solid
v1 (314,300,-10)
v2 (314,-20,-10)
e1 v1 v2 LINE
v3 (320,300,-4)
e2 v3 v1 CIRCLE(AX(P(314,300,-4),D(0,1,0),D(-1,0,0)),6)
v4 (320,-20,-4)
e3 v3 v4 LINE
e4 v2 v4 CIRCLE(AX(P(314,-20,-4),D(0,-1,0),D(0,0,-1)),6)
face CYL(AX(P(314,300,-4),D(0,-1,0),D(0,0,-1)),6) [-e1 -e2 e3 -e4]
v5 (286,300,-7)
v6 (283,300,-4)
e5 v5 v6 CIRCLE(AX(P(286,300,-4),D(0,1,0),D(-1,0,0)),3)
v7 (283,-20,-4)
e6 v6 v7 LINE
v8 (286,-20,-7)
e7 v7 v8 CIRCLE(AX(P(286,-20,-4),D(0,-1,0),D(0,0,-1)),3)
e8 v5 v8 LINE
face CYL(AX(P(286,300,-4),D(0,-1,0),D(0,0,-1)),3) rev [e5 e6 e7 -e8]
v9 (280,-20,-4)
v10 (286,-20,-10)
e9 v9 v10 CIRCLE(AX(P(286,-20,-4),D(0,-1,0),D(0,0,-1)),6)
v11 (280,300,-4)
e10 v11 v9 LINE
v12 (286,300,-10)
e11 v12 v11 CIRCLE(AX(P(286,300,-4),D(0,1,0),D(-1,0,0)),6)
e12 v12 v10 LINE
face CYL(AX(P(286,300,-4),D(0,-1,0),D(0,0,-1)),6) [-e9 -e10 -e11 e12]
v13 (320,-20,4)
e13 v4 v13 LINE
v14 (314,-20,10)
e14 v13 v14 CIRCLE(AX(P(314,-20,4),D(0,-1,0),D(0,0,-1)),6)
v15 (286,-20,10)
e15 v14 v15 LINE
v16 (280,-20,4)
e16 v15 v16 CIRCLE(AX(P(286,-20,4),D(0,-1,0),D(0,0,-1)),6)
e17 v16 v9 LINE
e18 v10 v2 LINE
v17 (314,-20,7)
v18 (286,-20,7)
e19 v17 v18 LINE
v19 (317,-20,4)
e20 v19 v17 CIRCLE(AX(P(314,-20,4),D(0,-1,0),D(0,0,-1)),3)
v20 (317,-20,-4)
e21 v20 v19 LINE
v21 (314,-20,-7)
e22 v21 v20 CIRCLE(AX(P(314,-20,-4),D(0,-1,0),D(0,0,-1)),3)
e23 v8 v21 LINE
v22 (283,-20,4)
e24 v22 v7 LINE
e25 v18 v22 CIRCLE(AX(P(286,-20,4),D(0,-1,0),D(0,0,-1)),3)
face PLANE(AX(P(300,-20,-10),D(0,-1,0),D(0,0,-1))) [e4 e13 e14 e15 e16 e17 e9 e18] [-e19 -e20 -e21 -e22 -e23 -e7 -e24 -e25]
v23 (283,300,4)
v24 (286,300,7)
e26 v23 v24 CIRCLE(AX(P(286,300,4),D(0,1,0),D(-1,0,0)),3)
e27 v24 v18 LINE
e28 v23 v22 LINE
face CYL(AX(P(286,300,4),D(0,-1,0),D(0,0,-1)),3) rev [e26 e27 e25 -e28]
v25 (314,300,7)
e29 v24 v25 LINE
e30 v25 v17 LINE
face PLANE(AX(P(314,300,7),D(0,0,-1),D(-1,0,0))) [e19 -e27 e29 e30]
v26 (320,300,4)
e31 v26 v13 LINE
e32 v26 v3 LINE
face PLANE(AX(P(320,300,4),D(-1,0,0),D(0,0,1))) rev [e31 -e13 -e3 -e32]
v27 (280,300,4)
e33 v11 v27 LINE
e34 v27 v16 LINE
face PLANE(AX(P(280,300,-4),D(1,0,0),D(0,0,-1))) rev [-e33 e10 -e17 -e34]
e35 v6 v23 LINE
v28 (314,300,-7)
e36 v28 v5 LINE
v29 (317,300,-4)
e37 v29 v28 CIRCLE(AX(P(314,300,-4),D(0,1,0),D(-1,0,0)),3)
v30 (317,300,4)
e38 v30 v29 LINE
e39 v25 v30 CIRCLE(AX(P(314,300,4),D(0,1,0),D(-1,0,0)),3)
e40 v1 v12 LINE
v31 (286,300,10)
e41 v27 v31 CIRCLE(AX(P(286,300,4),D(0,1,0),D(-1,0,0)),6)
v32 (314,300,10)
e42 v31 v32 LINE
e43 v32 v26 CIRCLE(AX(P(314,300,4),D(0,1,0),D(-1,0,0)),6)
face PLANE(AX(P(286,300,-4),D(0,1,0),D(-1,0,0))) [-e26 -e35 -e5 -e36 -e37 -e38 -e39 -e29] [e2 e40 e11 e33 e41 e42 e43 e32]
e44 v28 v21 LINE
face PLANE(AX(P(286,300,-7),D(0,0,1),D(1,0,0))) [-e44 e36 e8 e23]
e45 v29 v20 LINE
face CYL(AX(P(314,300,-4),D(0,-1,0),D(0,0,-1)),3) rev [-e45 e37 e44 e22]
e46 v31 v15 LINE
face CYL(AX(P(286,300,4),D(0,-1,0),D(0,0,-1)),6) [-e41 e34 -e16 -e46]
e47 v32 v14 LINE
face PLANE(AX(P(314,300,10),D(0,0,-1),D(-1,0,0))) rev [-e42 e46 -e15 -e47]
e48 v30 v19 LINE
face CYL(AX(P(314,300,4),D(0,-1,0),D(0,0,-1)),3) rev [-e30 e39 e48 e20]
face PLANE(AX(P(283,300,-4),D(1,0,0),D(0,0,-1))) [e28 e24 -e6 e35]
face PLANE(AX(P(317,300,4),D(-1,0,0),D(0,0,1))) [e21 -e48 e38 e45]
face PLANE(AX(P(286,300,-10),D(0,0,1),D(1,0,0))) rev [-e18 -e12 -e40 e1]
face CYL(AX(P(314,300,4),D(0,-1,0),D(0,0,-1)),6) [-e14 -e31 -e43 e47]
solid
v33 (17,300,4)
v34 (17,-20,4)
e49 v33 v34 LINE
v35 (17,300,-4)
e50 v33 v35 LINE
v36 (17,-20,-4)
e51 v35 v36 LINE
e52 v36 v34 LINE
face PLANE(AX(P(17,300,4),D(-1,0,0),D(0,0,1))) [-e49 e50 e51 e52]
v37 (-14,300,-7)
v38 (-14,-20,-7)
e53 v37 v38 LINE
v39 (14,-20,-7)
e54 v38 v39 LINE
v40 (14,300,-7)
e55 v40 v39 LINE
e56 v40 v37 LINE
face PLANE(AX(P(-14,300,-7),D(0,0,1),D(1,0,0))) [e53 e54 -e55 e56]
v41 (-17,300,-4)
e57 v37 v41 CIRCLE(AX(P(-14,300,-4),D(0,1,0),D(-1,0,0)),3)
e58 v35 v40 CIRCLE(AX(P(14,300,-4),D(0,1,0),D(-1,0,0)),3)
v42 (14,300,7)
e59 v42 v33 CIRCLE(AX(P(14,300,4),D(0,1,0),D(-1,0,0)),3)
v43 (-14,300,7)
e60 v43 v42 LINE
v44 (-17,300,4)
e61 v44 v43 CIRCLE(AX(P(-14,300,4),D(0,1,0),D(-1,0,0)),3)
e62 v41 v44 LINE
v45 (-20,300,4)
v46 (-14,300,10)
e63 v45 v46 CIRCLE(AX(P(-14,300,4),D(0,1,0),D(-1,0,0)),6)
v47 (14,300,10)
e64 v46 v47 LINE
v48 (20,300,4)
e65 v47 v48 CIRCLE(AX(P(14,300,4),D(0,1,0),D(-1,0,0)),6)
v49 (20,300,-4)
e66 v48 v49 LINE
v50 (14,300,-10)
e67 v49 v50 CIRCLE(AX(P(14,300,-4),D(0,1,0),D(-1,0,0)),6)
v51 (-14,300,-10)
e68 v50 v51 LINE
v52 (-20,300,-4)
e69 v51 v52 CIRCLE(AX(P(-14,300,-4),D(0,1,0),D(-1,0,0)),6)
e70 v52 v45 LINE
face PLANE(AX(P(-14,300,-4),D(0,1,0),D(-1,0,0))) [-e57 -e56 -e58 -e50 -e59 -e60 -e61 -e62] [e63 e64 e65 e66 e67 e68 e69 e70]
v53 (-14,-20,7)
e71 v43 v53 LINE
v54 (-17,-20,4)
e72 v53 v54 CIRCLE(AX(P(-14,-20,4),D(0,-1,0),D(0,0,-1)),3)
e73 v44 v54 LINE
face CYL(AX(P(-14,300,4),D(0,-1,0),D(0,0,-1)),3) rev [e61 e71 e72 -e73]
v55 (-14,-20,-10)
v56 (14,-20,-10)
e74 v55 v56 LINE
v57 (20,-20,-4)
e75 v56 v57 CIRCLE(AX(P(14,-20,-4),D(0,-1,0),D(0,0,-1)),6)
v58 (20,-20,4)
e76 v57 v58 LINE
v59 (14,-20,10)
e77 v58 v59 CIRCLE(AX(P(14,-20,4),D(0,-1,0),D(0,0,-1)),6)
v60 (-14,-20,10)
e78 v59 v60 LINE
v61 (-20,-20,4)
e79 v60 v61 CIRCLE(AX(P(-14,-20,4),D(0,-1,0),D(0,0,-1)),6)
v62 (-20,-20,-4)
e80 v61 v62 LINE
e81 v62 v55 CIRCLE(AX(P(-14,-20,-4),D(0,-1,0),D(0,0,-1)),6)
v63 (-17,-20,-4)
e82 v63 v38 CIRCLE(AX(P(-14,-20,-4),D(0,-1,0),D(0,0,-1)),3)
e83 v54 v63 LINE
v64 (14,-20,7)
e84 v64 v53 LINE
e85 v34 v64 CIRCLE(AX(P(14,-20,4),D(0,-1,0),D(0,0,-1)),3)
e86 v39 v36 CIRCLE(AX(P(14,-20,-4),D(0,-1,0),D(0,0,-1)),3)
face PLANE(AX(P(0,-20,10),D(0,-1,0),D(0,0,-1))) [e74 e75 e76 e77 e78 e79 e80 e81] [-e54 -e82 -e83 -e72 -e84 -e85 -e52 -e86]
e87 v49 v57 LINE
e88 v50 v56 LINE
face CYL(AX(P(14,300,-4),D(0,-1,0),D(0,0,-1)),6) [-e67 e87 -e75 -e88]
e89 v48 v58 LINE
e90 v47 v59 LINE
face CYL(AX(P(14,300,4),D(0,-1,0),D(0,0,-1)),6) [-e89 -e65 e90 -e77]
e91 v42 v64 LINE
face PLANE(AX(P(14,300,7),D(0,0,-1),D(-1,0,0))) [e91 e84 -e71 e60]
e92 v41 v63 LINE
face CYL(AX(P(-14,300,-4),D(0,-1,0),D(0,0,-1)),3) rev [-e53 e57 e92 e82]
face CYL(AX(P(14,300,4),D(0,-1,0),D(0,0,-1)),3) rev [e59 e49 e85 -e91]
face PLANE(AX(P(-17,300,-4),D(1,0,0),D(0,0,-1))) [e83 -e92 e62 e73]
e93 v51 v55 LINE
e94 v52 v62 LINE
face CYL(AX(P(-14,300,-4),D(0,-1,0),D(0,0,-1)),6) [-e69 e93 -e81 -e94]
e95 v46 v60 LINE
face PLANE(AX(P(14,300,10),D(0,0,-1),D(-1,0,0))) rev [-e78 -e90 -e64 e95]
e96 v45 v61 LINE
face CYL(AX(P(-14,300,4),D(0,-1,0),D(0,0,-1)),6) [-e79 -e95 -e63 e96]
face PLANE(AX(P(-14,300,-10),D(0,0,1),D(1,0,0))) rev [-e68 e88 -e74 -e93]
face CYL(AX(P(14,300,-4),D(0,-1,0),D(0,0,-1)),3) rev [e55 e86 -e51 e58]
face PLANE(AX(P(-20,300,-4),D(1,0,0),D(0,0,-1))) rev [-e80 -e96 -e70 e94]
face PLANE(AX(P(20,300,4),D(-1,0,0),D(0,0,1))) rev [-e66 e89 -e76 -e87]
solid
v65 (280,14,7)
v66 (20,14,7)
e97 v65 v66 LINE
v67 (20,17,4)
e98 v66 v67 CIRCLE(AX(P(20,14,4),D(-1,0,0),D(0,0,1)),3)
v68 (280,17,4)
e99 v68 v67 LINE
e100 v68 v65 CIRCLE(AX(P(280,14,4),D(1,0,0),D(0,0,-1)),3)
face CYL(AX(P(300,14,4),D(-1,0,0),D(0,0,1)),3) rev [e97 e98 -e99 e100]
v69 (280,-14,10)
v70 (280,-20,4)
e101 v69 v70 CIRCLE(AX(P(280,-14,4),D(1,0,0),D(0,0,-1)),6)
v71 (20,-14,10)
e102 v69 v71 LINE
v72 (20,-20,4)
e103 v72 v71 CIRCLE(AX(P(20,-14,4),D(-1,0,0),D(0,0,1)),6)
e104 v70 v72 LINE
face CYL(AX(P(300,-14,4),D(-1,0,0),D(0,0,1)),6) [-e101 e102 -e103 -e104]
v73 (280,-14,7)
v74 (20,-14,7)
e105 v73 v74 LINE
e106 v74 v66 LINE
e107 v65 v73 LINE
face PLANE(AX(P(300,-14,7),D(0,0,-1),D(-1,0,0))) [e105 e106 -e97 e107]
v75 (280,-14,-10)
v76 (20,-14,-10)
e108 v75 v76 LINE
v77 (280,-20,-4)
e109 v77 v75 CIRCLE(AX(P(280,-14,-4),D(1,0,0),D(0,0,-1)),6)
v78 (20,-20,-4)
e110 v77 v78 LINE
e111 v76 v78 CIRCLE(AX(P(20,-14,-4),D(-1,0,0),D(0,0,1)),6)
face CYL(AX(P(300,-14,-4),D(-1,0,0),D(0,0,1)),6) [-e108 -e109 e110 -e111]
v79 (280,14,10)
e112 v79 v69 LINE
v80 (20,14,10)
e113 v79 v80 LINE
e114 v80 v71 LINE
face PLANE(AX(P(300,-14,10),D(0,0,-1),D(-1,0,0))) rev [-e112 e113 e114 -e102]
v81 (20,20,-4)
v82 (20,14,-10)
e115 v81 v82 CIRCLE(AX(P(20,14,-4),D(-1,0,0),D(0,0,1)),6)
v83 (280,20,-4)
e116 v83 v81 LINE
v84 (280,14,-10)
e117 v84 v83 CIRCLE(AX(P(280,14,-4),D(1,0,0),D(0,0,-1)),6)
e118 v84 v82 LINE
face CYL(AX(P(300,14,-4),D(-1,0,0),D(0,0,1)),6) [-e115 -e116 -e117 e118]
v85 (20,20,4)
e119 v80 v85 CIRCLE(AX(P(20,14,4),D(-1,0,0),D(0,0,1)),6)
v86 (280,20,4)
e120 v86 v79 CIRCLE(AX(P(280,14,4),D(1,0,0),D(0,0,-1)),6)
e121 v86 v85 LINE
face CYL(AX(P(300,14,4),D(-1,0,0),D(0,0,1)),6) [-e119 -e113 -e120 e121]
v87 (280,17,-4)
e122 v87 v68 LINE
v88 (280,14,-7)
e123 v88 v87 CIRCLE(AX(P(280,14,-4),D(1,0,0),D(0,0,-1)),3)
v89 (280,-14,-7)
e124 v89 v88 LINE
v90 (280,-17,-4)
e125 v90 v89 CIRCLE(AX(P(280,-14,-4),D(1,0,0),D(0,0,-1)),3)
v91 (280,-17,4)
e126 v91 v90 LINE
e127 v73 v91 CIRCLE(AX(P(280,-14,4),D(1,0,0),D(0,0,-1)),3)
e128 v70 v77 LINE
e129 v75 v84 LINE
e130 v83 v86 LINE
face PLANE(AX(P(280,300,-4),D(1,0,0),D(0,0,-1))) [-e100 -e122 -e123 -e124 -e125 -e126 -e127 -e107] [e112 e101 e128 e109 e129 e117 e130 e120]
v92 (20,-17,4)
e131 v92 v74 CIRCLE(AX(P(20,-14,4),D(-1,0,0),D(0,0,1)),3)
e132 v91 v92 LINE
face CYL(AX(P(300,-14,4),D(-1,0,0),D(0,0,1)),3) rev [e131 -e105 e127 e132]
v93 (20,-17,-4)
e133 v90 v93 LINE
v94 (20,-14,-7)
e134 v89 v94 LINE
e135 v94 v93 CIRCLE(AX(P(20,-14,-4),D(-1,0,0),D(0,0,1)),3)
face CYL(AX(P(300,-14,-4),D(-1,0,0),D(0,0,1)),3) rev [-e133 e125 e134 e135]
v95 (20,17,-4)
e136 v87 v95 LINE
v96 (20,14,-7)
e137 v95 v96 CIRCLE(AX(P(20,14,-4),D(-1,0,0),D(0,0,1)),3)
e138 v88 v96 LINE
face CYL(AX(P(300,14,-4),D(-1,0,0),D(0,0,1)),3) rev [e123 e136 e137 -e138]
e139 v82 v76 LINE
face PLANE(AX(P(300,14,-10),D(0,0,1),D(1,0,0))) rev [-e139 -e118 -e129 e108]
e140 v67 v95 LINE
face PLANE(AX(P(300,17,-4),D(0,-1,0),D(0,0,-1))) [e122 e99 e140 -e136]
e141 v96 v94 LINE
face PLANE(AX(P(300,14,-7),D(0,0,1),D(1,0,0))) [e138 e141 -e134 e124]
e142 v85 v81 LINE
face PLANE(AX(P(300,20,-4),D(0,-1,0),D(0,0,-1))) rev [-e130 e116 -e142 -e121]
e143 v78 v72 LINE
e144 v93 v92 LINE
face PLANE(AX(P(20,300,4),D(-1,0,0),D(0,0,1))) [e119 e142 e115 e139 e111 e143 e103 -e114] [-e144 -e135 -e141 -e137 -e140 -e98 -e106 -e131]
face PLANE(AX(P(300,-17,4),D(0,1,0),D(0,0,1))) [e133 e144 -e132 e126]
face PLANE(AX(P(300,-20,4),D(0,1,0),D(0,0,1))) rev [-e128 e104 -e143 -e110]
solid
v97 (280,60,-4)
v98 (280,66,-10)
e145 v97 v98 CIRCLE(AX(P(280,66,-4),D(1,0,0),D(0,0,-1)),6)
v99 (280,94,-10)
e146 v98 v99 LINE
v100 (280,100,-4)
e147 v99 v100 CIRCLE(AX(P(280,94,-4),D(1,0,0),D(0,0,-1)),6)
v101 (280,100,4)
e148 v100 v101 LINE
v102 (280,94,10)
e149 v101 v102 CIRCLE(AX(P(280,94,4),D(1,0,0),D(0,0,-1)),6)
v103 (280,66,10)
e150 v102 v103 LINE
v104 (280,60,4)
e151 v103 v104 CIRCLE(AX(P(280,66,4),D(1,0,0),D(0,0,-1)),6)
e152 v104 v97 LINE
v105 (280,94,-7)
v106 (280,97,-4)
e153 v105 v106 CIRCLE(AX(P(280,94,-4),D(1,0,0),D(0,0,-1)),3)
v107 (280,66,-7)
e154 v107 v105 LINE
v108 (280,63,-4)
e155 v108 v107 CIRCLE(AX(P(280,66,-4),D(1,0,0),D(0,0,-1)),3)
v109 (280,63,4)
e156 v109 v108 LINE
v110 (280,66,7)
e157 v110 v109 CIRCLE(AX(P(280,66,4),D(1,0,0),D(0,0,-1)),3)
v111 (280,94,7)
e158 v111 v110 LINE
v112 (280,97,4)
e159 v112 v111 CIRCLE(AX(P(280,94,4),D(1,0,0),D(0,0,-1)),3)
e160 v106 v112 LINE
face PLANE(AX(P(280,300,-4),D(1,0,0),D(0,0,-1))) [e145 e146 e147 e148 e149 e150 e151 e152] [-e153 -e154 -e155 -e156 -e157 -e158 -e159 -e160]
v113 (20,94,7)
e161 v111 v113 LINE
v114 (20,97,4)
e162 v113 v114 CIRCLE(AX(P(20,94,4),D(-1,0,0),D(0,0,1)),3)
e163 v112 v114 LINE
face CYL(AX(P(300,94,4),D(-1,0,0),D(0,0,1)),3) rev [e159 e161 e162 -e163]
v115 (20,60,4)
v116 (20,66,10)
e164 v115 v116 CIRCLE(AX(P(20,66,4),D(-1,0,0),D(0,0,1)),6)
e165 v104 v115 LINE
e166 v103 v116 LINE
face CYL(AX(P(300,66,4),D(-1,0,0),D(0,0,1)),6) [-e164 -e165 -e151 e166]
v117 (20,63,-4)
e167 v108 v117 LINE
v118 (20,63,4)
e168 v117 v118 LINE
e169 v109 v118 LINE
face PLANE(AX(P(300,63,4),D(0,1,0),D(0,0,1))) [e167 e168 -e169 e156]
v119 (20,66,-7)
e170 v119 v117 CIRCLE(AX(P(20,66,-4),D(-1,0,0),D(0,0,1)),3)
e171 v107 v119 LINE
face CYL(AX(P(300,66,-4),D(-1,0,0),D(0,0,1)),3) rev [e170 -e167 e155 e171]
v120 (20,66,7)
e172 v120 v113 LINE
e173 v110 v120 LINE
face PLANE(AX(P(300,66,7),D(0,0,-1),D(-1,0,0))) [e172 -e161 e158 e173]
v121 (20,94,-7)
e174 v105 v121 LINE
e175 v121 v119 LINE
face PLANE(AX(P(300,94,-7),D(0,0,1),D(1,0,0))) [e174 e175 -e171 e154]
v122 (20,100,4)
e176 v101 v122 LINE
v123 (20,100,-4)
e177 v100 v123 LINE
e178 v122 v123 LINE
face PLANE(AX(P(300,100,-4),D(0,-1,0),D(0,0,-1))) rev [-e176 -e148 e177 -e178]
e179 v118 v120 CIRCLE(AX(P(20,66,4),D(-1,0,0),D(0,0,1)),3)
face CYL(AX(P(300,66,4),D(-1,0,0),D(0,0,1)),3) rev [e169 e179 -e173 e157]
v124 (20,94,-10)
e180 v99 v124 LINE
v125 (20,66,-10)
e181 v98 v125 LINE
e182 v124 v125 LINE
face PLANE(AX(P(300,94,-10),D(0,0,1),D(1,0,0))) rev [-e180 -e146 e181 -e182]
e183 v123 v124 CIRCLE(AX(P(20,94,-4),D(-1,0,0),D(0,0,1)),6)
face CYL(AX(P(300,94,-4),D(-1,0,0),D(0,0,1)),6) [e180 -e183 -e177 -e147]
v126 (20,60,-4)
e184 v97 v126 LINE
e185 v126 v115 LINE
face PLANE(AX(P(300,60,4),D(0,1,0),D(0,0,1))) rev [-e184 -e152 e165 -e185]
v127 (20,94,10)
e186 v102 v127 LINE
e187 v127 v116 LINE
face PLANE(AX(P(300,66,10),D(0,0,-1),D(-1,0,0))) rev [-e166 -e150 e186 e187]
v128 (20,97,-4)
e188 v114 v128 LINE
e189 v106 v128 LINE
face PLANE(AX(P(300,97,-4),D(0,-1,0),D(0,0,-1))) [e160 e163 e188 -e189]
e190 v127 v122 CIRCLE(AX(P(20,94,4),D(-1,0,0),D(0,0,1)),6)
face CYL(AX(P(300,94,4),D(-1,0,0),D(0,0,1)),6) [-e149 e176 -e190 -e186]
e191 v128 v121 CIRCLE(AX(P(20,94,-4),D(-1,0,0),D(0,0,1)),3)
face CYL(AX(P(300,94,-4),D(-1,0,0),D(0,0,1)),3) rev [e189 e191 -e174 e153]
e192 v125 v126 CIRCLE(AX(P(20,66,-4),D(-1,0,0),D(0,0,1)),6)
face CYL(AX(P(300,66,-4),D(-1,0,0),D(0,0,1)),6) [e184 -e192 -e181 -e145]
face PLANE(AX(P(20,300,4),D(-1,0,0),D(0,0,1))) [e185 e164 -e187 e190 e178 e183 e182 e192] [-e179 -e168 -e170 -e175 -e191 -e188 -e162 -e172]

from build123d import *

# Parameters (mm, degrees)
F_40_X_20_X_3_1_DEPTH      = 300
F_40_X_20_X_3_1_DEPTH_BACK = 20
F_40_X_20_X_3_1_2_DEPTH    = 320
F_40_X_20_X_3_1_3_DEPTH    = 302
F_40_X_20_X_3_1_4_DEPTH    = 302


with BuildPart() as part:
    # Sketch1 → 矩形管 40 X 20 X 3(1) (new, two sides: drawn at the far end of the back side and taken through both)
    with BuildSketch(Plane(origin=(0, 0, 0), x_dir=(0, 0, -1), z_dir=(0, 1, 0)).offset(-F_40_X_20_X_3_1_DEPTH_BACK)):
        with BuildLine():
            Line((-4, -20), (4, -20))
            ThreePointArc((4, -20), (8.242640687, -18.242640687), (10, -14))
            Line((10, -14), (10, 14))
            ThreePointArc((10, 14), (8.242640687, 18.242640687), (4, 20))
            Line((4, 20), (-4, 20))
            ThreePointArc((-4, 20), (-8.242640687, 18.242640687), (-10, 14))
            Line((-10, 14), (-10, -14))
            ThreePointArc((-10, -14), (-8.242640687, -18.242640687), (-4, -20))
        make_face()
        with BuildLine():
            Line((-4, -17), (4, -17))
            ThreePointArc((4, -17), (6.121320344, -16.121320344), (7, -14))
            Line((7, -14), (7, 14))
            ThreePointArc((7, 14), (6.121320344, 16.121320344), (4, 17))
            Line((4, 17), (-4, 17))
            ThreePointArc((-4, 17), (-6.121320344, 16.121320344), (-7, 14))
            Line((-7, 14), (-7, -14))
            ThreePointArc((-7, -14), (-6.121320344, -16.121320344), (-4, -17))
        make_face(mode=Mode.SUBTRACT)
    extrude(amount=F_40_X_20_X_3_1_DEPTH + F_40_X_20_X_3_1_DEPTH_BACK)


with BuildPart() as body_2:
    # Sketch1 on segment 2 (carried to segment 2) → 40 X 20 X 3_1 2 (new body)
    with BuildSketch(Plane(origin=(300, -20, 0), x_dir=(0, 0, -1), z_dir=(0, 1, 0))):
        with BuildLine():
            Line((-4, -20), (4, -20))
            ThreePointArc((4, -20), (8.242640687, -18.242640687), (10, -14))
            Line((10, -14), (10, 14))
            ThreePointArc((10, 14), (8.242640687, 18.242640687), (4, 20))
            Line((4, 20), (-4, 20))
            ThreePointArc((-4, 20), (-8.242640687, 18.242640687), (-10, 14))
            Line((-10, 14), (-10, -14))
            ThreePointArc((-10, -14), (-8.242640687, -18.242640687), (-4, -20))
        make_face()
        with BuildLine():
            Line((-4, -17), (4, -17))
            ThreePointArc((4, -17), (6.121320344, -16.121320344), (7, -14))
            Line((7, -14), (7, 14))
            ThreePointArc((7, 14), (6.121320344, 16.121320344), (4, 17))
            Line((4, 17), (-4, 17))
            ThreePointArc((-4, 17), (-6.121320344, 16.121320344), (-7, 14))
            Line((-7, 14), (-7, -14))
            ThreePointArc((-7, -14), (-6.121320344, -16.121320344), (-4, -17))
        make_face(mode=Mode.SUBTRACT)
    extrude(amount=F_40_X_20_X_3_1_2_DEPTH)


with BuildPart() as body_3:
    # Sketch1 on segment 3 (carried to segment 3) → 40 X 20 X 3_1 3 (new body)
    with BuildSketch(Plane(origin=(-1, 0, 0), x_dir=(0, 0, -1), z_dir=(1, 0, 0))):
        with BuildLine():
            Line((-4, -20), (4, -20))
            ThreePointArc((4, -20), (8.242640687, -18.242640687), (10, -14))
            Line((10, -14), (10, 14))
            ThreePointArc((10, 14), (8.242640687, 18.242640687), (4, 20))
            Line((4, 20), (-4, 20))
            ThreePointArc((-4, 20), (-8.242640687, 18.242640687), (-10, 14))
            Line((-10, 14), (-10, -14))
            ThreePointArc((-10, -14), (-8.242640687, -18.242640687), (-4, -20))
        make_face()
        with BuildLine():
            Line((-4, -17), (4, -17))
            ThreePointArc((4, -17), (6.121320344, -16.121320344), (7, -14))
            Line((7, -14), (7, 14))
            ThreePointArc((7, 14), (6.121320344, 16.121320344), (4, 17))
            Line((4, 17), (-4, 17))
            ThreePointArc((-4, 17), (-6.121320344, 16.121320344), (-7, 14))
            Line((-7, 14), (-7, -14))
            ThreePointArc((-7, -14), (-6.121320344, -16.121320344), (-4, -17))
        make_face(mode=Mode.SUBTRACT)
    extrude(amount=F_40_X_20_X_3_1_3_DEPTH)

    # 40 X 20 X 3_1 3 end butt 1
    split(bisect_by=Plane.YZ.offset(20), keep=Keep.TOP)

    # 40 X 20 X 3_1 3 end butt 2
    split(bisect_by=Plane(origin=(280, 0, 0), x_dir=(0, -1, 0), z_dir=(-1, 0, 0)), keep=Keep.TOP)


with BuildPart() as body_4:
    # Sketch1 on segment 4 (carried to segment 4) → 40 X 20 X 3_1 4 (new body)
    with BuildSketch(Plane(origin=(-1, 80, 0), x_dir=(0, 0, -1), z_dir=(1, 0, 0))):
        with BuildLine():
            Line((-4, -20), (4, -20))
            ThreePointArc((4, -20), (8.242640687, -18.242640687), (10, -14))
            Line((10, -14), (10, 14))
            ThreePointArc((10, 14), (8.242640687, 18.242640687), (4, 20))
            Line((4, 20), (-4, 20))
            ThreePointArc((-4, 20), (-8.242640687, 18.242640687), (-10, 14))
            Line((-10, 14), (-10, -14))
            ThreePointArc((-10, -14), (-8.242640687, -18.242640687), (-4, -20))
        make_face()
        with BuildLine():
            Line((-4, -17), (4, -17))
            ThreePointArc((4, -17), (6.121320344, -16.121320344), (7, -14))
            Line((7, -14), (7, 14))
            ThreePointArc((7, 14), (6.121320344, 16.121320344), (4, 17))
            Line((4, 17), (-4, 17))
            ThreePointArc((-4, 17), (-6.121320344, 16.121320344), (-7, 14))
            Line((-7, 14), (-7, -14))
            ThreePointArc((-7, -14), (-6.121320344, -16.121320344), (-4, -17))
        make_face(mode=Mode.SUBTRACT)
    extrude(amount=F_40_X_20_X_3_1_4_DEPTH)

    # 40 X 20 X 3_1 4 end butt 1
    split(bisect_by=Plane(origin=(20, 80, 0), x_dir=(0, 1, 0), z_dir=(1, 0, 0)), keep=Keep.TOP)

    # 40 X 20 X 3_1 4 end butt 2
    split(bisect_by=Plane(origin=(280, 80, 0), x_dir=(0, -1, 0), z_dir=(-1, 0, 0)), keep=Keep.TOP)


solid = Compound([part.part, body_2.part, body_3.part, body_4.part])
